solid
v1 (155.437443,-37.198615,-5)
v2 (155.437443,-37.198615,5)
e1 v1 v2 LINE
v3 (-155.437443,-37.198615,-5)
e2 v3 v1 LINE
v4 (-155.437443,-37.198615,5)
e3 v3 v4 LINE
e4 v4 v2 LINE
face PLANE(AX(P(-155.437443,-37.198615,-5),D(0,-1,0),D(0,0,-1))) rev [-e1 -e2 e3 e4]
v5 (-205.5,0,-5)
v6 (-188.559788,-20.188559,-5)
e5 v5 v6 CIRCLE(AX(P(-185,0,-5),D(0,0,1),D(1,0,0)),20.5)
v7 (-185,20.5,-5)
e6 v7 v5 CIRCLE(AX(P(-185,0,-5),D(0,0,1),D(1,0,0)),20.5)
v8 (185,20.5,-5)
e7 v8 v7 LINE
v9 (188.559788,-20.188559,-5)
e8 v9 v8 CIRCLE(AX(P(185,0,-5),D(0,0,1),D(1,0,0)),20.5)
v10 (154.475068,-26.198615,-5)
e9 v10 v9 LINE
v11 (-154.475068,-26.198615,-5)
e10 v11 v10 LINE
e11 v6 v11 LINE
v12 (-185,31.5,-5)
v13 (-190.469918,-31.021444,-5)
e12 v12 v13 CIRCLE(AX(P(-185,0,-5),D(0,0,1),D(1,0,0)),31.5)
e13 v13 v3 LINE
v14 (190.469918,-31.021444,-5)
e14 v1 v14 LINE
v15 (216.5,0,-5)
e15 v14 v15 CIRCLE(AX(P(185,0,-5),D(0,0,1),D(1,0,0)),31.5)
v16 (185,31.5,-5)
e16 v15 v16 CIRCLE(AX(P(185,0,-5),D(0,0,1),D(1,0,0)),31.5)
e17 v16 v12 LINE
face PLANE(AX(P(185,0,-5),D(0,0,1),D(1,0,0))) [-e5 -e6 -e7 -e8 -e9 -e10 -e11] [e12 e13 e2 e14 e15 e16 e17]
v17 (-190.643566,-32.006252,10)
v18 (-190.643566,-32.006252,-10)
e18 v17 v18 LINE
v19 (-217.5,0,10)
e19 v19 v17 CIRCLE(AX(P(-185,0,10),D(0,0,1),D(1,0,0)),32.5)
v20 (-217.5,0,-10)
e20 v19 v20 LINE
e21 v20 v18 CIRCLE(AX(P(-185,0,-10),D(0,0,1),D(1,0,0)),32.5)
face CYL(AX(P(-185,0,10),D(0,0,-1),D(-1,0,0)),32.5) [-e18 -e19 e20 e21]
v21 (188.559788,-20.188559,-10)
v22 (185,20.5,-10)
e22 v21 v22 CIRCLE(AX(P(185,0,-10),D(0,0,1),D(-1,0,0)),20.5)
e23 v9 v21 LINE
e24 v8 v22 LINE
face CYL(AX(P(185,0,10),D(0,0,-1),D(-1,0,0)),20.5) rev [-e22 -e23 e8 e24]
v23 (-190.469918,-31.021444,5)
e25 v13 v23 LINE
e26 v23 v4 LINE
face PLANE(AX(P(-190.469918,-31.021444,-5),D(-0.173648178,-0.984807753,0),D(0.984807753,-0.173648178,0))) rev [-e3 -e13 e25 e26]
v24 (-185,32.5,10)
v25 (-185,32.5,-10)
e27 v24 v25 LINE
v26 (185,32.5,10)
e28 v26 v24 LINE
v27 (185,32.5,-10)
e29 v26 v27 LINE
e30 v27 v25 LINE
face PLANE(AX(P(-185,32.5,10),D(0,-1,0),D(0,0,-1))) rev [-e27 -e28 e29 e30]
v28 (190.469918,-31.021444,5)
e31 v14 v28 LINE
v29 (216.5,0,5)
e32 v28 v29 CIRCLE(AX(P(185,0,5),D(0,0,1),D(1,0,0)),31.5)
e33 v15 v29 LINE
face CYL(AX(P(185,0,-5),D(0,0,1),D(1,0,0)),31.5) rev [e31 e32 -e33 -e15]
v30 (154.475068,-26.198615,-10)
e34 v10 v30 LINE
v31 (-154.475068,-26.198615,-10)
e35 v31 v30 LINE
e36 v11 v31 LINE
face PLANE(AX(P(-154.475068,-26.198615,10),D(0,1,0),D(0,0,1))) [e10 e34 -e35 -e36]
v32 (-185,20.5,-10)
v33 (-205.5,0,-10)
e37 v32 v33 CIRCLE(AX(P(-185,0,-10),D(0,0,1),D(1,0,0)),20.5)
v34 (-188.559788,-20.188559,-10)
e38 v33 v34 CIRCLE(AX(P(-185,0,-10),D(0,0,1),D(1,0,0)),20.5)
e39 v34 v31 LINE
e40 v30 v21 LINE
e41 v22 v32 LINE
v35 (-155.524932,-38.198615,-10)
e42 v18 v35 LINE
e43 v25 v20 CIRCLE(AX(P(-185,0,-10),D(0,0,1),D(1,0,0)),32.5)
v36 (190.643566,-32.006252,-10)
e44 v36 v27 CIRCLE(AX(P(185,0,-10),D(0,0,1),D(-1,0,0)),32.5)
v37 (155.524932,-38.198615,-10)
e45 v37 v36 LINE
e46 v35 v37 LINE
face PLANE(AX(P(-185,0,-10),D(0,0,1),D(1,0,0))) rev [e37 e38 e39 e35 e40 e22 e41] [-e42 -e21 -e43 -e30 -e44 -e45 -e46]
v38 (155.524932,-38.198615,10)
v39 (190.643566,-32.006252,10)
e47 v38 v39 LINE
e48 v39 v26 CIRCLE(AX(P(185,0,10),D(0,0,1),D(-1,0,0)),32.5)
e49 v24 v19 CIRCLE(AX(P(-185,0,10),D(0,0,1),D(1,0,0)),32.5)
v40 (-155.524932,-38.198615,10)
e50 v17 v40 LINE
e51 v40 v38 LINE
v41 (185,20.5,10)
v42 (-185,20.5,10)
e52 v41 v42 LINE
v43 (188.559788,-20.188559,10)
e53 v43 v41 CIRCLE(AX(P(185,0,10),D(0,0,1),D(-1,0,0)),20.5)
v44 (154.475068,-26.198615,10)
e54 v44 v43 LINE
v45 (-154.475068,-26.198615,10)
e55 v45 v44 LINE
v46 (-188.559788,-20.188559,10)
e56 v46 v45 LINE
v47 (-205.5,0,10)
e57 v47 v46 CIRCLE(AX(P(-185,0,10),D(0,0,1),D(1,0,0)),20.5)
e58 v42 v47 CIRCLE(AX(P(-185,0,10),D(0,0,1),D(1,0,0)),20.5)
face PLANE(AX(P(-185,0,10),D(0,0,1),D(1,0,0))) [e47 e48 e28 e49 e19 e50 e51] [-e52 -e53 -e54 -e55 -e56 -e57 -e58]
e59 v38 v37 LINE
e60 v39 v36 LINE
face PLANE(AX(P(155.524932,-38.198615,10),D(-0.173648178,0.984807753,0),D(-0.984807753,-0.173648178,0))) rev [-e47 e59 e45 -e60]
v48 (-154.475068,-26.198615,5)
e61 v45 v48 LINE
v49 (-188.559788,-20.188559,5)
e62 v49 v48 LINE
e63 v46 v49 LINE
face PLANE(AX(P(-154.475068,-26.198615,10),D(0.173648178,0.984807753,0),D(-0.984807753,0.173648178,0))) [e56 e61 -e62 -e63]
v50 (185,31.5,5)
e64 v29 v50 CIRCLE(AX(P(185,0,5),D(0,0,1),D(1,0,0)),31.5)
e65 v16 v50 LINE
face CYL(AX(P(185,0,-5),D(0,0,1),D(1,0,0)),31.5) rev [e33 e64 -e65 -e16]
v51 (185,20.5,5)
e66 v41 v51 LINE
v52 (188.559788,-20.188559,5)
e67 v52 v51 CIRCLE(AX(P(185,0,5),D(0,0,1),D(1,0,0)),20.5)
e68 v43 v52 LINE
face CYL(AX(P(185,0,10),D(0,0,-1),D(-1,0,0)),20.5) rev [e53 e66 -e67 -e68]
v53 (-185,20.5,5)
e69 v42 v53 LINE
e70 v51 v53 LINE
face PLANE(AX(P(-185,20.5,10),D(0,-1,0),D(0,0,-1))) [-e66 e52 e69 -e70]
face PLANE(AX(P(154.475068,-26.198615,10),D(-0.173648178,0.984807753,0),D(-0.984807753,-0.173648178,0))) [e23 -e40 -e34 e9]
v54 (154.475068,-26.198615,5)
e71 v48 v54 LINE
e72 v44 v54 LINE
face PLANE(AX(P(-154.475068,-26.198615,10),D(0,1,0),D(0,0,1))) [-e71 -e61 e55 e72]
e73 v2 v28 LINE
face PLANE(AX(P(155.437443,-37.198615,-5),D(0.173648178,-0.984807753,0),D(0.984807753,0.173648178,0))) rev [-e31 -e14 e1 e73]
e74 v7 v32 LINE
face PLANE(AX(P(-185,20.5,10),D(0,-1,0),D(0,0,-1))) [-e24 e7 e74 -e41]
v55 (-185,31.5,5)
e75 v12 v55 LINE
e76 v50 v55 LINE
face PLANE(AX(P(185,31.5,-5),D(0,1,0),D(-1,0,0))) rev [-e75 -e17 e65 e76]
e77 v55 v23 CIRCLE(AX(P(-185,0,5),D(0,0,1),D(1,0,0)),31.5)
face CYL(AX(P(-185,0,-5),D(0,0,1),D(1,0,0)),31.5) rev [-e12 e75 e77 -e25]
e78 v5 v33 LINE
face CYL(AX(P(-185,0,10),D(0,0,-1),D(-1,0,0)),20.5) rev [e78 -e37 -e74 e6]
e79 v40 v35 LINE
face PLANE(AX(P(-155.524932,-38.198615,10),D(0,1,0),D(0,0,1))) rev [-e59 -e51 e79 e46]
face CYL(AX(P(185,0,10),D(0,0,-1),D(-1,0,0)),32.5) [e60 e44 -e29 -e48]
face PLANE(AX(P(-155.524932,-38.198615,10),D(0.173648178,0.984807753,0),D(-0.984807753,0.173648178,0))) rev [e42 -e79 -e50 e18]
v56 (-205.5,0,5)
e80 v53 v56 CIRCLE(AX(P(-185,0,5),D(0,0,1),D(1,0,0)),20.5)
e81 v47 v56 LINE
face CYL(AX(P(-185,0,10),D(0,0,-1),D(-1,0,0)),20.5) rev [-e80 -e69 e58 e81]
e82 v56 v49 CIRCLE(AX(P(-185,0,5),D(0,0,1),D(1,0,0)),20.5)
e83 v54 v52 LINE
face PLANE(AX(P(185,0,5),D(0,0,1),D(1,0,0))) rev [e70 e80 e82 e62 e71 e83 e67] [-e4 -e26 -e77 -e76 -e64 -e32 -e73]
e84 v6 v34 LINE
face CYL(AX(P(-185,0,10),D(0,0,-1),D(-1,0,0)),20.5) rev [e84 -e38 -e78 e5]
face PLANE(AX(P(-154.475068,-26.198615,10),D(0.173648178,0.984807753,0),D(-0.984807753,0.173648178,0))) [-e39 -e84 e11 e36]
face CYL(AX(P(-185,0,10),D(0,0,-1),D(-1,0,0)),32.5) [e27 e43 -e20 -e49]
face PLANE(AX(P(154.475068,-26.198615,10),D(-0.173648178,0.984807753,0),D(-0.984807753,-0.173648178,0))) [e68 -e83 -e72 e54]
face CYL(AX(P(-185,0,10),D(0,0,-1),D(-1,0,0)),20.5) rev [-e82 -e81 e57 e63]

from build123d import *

# Parameters (mm, degrees)
BOSS_EXTRUDE1_DEPTH = 10
CUT_EXTRUDE1_DEPTH  = 5


with BuildPart() as part:
    # Sketch2 → Boss-Extrude1 (new, symmetric)
    with BuildSketch(Plane.XY):
        with BuildLine():
            Line((-185, 32.5), (185, 32.5))
            ThreePointArc((185, 32.5), (217.376327688, 2.832561639), (190.643565774, -32.006251973))
            Line((190.643565774, -32.006251973), (155.524931981, -38.198614636))
            Line((155.524931981, -38.198614636), (-155.524931981, -38.198614636))
            Line((-155.524931981, -38.198614636), (-190.643565774, -32.006251973))
            ThreePointArc((-190.643565774, -32.006251973), (-217.376327688, 2.832561639), (-185, 32.5))
        make_face()
        with BuildLine():
            Line((-185, 20.5), (185, 20.5))
            ThreePointArc((185, 20.5), (205.421991311, 1.786692726), (188.559787642, -20.188558937))
            Line((188.559787642, -20.188558937), (154.475068019, -26.198614636))
            Line((154.475068019, -26.198614636), (-154.475068019, -26.198614636))
            Line((-154.475068019, -26.198614636), (-188.559787642, -20.188558937))
            ThreePointArc((-188.559787642, -20.188558937), (-205.421991311, 1.786692726), (-185, 20.5))
        make_face(mode=Mode.SUBTRACT)
    extrude(amount=BOSS_EXTRUDE1_DEPTH, both=True)

    # Sketch8 → Cut-Extrude1 (cut, symmetric)
    with BuildSketch(Plane.XY):
        with BuildLine():
            Line((155.437443318, -37.198614636), (190.469917597, -31.02144422))
            ThreePointArc((190.469917597, -31.02144422), (216.38013299, 2.745405897), (185, 31.5))
            Line((185, 31.5), (-185, 31.5))
            ThreePointArc((-185, 31.5), (-216.38013299, 2.745405897), (-190.469917597, -31.02144422))
            Line((-190.469917597, -31.02144422), (-155.437443318, -37.198614636))
            Line((-155.437443318, -37.198614636), (155.437443318, -37.198614636))
        make_face()
    extrude(amount=CUT_EXTRUDE1_DEPTH, both=True, mode=Mode.SUBTRACT)


solid = part.part
